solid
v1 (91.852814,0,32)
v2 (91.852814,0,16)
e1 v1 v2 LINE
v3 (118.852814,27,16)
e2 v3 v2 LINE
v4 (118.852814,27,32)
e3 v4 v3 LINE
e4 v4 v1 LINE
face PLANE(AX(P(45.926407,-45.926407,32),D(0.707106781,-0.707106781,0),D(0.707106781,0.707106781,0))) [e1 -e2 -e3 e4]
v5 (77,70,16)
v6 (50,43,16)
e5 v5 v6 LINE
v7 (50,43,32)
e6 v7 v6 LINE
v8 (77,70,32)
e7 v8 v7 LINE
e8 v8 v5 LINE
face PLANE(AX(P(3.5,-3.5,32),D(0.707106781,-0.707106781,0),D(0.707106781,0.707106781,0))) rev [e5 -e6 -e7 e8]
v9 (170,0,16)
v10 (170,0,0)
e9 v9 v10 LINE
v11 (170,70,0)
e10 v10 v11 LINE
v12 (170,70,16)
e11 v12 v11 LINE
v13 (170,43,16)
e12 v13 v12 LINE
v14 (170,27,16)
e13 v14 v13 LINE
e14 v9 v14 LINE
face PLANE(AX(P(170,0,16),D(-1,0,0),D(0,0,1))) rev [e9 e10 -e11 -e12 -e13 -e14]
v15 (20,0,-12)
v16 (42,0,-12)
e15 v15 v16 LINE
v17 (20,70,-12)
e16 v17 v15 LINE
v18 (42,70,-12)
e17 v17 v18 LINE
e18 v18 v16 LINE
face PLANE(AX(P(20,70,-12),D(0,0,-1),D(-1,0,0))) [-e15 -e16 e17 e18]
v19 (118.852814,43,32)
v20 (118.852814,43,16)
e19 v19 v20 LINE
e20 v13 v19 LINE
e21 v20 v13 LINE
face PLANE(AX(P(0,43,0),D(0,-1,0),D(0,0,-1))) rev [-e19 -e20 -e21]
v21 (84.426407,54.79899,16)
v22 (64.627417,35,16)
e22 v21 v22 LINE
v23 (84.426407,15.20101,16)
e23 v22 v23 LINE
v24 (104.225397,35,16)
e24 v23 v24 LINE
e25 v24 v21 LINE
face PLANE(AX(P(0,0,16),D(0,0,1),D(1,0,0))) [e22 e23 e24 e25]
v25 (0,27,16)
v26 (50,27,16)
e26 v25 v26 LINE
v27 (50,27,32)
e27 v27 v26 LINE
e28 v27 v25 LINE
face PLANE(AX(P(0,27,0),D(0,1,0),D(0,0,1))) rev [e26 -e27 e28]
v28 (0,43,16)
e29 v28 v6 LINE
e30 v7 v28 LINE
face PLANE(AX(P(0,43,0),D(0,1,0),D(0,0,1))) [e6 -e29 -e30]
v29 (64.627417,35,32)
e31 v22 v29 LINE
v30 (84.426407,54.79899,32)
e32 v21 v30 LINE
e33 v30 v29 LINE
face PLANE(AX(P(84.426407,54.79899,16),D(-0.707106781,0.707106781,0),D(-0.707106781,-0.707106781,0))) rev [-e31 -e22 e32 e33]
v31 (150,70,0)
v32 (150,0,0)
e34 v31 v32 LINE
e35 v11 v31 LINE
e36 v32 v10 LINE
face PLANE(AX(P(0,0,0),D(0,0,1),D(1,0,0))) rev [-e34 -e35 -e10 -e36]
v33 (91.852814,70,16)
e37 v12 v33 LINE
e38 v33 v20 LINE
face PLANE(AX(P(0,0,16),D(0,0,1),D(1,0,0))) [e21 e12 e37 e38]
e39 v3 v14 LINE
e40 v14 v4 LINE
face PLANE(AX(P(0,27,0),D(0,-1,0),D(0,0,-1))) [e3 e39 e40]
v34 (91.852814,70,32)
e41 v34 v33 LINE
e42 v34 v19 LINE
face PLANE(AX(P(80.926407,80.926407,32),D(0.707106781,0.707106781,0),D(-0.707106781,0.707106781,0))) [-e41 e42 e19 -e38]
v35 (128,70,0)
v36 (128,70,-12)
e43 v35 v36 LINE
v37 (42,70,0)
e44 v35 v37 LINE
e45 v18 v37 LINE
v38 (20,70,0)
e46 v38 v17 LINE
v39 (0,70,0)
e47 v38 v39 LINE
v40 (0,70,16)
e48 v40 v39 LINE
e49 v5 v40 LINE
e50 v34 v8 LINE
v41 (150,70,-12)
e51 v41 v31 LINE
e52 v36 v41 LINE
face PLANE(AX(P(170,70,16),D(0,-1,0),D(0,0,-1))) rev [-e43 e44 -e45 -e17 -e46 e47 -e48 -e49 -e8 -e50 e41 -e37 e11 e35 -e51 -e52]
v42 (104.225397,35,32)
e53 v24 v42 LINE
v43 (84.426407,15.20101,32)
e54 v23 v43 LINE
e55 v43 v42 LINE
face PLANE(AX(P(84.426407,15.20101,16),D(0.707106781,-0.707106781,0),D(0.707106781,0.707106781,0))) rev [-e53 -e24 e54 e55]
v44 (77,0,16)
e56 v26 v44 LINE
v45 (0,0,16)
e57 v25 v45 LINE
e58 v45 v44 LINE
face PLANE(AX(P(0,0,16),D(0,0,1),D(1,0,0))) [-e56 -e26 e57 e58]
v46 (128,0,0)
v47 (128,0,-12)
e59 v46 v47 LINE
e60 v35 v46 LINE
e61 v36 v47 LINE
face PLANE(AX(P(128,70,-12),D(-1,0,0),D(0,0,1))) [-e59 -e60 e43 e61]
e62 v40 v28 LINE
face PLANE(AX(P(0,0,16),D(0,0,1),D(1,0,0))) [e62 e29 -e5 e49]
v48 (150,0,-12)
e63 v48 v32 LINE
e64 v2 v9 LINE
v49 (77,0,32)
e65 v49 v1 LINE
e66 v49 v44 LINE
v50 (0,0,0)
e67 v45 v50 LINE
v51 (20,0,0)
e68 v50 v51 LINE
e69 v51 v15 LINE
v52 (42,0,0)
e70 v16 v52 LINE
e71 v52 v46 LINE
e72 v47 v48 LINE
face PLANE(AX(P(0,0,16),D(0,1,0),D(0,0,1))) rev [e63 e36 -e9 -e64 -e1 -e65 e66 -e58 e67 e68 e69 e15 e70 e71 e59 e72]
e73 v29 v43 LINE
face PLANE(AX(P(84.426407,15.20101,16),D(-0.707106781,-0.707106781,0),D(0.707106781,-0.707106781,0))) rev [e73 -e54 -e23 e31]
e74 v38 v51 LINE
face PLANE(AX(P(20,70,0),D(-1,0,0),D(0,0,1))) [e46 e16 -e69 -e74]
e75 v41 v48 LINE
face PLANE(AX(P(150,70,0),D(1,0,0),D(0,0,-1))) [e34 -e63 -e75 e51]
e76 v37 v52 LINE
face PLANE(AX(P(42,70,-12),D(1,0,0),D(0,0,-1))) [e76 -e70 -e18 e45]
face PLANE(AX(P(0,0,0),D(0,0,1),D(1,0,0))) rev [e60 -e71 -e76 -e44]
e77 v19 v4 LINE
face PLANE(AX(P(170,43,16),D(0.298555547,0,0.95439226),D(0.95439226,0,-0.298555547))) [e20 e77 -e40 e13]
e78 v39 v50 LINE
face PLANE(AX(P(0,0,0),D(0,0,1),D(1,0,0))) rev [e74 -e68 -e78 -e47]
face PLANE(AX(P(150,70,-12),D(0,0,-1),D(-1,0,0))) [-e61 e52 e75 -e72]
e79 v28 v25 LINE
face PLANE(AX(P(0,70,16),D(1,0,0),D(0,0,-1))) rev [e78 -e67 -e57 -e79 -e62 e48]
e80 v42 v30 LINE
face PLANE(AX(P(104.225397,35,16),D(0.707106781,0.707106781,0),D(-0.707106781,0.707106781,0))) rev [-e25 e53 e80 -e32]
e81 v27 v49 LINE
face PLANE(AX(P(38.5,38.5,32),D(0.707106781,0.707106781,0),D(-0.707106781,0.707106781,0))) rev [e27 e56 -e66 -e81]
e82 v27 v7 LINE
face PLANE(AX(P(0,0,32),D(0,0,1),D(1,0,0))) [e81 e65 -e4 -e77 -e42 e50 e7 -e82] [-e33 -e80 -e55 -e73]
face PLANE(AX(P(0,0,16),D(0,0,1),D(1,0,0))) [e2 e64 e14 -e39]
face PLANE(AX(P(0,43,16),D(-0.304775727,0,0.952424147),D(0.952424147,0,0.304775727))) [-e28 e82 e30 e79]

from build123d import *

# Parameters (mm, degrees)
BASE_PLATE_SKETCH_W      = 170
BASE_PLATE_SKETCH_H      = 70
BASE_PLATE_16MM_DEPTH    = 16
CENTER_BOSS_60X60_DEPTH  = 16
CENTER_POCKET_28_DEPTH   = 16
LEFT_WEDGE_BOSS_DEPTH    = 43
LEFT_WEDGE_CUT_DEPTH     = 27
RIGHT_WEDGE_BOSS_DEPTH   = 43
RIGHT_WEDGE_CUT_DEPTH    = 27
TOP_RAIL_SKETCH_W        = 22
TOP_RAIL_SKETCH_H        = 12
TOP_RAIL_WITH_TABS_DEPTH = 70


with BuildPart() as part:
    # Base Plate Sketch → Base Plate 16mm (new body)
    with BuildSketch(Plane.XY):
        with Locations((85, 35)):
            Rectangle(BASE_PLATE_SKETCH_W, BASE_PLATE_SKETCH_H)
    extrude(amount=BASE_PLATE_16MM_DEPTH)

    # Center Boss Sketch → Center Boss 60x60 (add)
    with BuildSketch(Plane.XY.offset(16)):
        Polygon((91.852813742, 70), (85, 70), (77, 70), (50, 43), (50, 35), (50, 27), (77, 0), (85, 0), (91.852813742, 0), (118.852813742, 27), (118.852813742, 35), (118.852813742, 43), align=None)
    extrude(amount=CENTER_BOSS_60X60_DEPTH)

    # Center Pocket Sketch → Center Pocket 28 (cut)
    with BuildSketch(Plane.XY.offset(32)):
        Polygon((84.426406871, 15.201010127), (104.225396744, 35), (84.426406871, 54.798989873), (64.627416998, 35), align=None)
    extrude(amount=-CENTER_POCKET_28_DEPTH, mode=Mode.SUBTRACT)

    # Left Wedge Sketch → Left Wedge Boss (add)
    with BuildSketch(Plane.XZ):
        Polygon((118.852813742, 32), (118.852813742, 16), (170, 16), align=None)
    extrude(amount=-LEFT_WEDGE_BOSS_DEPTH)

    # Left Wedge Cut Sketch → Left Wedge Cut (cut)
    with BuildSketch(Plane.XZ):
        Polygon((118.852813742, 32), (118.852813742, 16), (170, 16), align=None)
    extrude(amount=-LEFT_WEDGE_CUT_DEPTH, mode=Mode.SUBTRACT)

    # Right Wedge Sketch → Right Wedge Boss (add)
    with BuildSketch(Plane.XZ):
        Polygon((50, 32), (50, 16), (0, 16), align=None)
    extrude(amount=-RIGHT_WEDGE_BOSS_DEPTH)

    # Right Wedge Cut Sketch → Right Wedge Cut (cut)
    with BuildSketch(Plane.XZ):
        Polygon((50, 32), (50, 16), (0, 16), align=None)
    extrude(amount=-RIGHT_WEDGE_CUT_DEPTH, mode=Mode.SUBTRACT)

    # Top Rail Sketch → Top Rail with Tabs (add)
    with BuildSketch(Plane.XZ):
        with Locations((31, -6)):
            Rectangle(TOP_RAIL_SKETCH_W, TOP_RAIL_SKETCH_H)
        with Locations((139, -6)):
            Rectangle(TOP_RAIL_SKETCH_W, TOP_RAIL_SKETCH_H)
    extrude(amount=-TOP_RAIL_WITH_TABS_DEPTH)


solid = part.part
